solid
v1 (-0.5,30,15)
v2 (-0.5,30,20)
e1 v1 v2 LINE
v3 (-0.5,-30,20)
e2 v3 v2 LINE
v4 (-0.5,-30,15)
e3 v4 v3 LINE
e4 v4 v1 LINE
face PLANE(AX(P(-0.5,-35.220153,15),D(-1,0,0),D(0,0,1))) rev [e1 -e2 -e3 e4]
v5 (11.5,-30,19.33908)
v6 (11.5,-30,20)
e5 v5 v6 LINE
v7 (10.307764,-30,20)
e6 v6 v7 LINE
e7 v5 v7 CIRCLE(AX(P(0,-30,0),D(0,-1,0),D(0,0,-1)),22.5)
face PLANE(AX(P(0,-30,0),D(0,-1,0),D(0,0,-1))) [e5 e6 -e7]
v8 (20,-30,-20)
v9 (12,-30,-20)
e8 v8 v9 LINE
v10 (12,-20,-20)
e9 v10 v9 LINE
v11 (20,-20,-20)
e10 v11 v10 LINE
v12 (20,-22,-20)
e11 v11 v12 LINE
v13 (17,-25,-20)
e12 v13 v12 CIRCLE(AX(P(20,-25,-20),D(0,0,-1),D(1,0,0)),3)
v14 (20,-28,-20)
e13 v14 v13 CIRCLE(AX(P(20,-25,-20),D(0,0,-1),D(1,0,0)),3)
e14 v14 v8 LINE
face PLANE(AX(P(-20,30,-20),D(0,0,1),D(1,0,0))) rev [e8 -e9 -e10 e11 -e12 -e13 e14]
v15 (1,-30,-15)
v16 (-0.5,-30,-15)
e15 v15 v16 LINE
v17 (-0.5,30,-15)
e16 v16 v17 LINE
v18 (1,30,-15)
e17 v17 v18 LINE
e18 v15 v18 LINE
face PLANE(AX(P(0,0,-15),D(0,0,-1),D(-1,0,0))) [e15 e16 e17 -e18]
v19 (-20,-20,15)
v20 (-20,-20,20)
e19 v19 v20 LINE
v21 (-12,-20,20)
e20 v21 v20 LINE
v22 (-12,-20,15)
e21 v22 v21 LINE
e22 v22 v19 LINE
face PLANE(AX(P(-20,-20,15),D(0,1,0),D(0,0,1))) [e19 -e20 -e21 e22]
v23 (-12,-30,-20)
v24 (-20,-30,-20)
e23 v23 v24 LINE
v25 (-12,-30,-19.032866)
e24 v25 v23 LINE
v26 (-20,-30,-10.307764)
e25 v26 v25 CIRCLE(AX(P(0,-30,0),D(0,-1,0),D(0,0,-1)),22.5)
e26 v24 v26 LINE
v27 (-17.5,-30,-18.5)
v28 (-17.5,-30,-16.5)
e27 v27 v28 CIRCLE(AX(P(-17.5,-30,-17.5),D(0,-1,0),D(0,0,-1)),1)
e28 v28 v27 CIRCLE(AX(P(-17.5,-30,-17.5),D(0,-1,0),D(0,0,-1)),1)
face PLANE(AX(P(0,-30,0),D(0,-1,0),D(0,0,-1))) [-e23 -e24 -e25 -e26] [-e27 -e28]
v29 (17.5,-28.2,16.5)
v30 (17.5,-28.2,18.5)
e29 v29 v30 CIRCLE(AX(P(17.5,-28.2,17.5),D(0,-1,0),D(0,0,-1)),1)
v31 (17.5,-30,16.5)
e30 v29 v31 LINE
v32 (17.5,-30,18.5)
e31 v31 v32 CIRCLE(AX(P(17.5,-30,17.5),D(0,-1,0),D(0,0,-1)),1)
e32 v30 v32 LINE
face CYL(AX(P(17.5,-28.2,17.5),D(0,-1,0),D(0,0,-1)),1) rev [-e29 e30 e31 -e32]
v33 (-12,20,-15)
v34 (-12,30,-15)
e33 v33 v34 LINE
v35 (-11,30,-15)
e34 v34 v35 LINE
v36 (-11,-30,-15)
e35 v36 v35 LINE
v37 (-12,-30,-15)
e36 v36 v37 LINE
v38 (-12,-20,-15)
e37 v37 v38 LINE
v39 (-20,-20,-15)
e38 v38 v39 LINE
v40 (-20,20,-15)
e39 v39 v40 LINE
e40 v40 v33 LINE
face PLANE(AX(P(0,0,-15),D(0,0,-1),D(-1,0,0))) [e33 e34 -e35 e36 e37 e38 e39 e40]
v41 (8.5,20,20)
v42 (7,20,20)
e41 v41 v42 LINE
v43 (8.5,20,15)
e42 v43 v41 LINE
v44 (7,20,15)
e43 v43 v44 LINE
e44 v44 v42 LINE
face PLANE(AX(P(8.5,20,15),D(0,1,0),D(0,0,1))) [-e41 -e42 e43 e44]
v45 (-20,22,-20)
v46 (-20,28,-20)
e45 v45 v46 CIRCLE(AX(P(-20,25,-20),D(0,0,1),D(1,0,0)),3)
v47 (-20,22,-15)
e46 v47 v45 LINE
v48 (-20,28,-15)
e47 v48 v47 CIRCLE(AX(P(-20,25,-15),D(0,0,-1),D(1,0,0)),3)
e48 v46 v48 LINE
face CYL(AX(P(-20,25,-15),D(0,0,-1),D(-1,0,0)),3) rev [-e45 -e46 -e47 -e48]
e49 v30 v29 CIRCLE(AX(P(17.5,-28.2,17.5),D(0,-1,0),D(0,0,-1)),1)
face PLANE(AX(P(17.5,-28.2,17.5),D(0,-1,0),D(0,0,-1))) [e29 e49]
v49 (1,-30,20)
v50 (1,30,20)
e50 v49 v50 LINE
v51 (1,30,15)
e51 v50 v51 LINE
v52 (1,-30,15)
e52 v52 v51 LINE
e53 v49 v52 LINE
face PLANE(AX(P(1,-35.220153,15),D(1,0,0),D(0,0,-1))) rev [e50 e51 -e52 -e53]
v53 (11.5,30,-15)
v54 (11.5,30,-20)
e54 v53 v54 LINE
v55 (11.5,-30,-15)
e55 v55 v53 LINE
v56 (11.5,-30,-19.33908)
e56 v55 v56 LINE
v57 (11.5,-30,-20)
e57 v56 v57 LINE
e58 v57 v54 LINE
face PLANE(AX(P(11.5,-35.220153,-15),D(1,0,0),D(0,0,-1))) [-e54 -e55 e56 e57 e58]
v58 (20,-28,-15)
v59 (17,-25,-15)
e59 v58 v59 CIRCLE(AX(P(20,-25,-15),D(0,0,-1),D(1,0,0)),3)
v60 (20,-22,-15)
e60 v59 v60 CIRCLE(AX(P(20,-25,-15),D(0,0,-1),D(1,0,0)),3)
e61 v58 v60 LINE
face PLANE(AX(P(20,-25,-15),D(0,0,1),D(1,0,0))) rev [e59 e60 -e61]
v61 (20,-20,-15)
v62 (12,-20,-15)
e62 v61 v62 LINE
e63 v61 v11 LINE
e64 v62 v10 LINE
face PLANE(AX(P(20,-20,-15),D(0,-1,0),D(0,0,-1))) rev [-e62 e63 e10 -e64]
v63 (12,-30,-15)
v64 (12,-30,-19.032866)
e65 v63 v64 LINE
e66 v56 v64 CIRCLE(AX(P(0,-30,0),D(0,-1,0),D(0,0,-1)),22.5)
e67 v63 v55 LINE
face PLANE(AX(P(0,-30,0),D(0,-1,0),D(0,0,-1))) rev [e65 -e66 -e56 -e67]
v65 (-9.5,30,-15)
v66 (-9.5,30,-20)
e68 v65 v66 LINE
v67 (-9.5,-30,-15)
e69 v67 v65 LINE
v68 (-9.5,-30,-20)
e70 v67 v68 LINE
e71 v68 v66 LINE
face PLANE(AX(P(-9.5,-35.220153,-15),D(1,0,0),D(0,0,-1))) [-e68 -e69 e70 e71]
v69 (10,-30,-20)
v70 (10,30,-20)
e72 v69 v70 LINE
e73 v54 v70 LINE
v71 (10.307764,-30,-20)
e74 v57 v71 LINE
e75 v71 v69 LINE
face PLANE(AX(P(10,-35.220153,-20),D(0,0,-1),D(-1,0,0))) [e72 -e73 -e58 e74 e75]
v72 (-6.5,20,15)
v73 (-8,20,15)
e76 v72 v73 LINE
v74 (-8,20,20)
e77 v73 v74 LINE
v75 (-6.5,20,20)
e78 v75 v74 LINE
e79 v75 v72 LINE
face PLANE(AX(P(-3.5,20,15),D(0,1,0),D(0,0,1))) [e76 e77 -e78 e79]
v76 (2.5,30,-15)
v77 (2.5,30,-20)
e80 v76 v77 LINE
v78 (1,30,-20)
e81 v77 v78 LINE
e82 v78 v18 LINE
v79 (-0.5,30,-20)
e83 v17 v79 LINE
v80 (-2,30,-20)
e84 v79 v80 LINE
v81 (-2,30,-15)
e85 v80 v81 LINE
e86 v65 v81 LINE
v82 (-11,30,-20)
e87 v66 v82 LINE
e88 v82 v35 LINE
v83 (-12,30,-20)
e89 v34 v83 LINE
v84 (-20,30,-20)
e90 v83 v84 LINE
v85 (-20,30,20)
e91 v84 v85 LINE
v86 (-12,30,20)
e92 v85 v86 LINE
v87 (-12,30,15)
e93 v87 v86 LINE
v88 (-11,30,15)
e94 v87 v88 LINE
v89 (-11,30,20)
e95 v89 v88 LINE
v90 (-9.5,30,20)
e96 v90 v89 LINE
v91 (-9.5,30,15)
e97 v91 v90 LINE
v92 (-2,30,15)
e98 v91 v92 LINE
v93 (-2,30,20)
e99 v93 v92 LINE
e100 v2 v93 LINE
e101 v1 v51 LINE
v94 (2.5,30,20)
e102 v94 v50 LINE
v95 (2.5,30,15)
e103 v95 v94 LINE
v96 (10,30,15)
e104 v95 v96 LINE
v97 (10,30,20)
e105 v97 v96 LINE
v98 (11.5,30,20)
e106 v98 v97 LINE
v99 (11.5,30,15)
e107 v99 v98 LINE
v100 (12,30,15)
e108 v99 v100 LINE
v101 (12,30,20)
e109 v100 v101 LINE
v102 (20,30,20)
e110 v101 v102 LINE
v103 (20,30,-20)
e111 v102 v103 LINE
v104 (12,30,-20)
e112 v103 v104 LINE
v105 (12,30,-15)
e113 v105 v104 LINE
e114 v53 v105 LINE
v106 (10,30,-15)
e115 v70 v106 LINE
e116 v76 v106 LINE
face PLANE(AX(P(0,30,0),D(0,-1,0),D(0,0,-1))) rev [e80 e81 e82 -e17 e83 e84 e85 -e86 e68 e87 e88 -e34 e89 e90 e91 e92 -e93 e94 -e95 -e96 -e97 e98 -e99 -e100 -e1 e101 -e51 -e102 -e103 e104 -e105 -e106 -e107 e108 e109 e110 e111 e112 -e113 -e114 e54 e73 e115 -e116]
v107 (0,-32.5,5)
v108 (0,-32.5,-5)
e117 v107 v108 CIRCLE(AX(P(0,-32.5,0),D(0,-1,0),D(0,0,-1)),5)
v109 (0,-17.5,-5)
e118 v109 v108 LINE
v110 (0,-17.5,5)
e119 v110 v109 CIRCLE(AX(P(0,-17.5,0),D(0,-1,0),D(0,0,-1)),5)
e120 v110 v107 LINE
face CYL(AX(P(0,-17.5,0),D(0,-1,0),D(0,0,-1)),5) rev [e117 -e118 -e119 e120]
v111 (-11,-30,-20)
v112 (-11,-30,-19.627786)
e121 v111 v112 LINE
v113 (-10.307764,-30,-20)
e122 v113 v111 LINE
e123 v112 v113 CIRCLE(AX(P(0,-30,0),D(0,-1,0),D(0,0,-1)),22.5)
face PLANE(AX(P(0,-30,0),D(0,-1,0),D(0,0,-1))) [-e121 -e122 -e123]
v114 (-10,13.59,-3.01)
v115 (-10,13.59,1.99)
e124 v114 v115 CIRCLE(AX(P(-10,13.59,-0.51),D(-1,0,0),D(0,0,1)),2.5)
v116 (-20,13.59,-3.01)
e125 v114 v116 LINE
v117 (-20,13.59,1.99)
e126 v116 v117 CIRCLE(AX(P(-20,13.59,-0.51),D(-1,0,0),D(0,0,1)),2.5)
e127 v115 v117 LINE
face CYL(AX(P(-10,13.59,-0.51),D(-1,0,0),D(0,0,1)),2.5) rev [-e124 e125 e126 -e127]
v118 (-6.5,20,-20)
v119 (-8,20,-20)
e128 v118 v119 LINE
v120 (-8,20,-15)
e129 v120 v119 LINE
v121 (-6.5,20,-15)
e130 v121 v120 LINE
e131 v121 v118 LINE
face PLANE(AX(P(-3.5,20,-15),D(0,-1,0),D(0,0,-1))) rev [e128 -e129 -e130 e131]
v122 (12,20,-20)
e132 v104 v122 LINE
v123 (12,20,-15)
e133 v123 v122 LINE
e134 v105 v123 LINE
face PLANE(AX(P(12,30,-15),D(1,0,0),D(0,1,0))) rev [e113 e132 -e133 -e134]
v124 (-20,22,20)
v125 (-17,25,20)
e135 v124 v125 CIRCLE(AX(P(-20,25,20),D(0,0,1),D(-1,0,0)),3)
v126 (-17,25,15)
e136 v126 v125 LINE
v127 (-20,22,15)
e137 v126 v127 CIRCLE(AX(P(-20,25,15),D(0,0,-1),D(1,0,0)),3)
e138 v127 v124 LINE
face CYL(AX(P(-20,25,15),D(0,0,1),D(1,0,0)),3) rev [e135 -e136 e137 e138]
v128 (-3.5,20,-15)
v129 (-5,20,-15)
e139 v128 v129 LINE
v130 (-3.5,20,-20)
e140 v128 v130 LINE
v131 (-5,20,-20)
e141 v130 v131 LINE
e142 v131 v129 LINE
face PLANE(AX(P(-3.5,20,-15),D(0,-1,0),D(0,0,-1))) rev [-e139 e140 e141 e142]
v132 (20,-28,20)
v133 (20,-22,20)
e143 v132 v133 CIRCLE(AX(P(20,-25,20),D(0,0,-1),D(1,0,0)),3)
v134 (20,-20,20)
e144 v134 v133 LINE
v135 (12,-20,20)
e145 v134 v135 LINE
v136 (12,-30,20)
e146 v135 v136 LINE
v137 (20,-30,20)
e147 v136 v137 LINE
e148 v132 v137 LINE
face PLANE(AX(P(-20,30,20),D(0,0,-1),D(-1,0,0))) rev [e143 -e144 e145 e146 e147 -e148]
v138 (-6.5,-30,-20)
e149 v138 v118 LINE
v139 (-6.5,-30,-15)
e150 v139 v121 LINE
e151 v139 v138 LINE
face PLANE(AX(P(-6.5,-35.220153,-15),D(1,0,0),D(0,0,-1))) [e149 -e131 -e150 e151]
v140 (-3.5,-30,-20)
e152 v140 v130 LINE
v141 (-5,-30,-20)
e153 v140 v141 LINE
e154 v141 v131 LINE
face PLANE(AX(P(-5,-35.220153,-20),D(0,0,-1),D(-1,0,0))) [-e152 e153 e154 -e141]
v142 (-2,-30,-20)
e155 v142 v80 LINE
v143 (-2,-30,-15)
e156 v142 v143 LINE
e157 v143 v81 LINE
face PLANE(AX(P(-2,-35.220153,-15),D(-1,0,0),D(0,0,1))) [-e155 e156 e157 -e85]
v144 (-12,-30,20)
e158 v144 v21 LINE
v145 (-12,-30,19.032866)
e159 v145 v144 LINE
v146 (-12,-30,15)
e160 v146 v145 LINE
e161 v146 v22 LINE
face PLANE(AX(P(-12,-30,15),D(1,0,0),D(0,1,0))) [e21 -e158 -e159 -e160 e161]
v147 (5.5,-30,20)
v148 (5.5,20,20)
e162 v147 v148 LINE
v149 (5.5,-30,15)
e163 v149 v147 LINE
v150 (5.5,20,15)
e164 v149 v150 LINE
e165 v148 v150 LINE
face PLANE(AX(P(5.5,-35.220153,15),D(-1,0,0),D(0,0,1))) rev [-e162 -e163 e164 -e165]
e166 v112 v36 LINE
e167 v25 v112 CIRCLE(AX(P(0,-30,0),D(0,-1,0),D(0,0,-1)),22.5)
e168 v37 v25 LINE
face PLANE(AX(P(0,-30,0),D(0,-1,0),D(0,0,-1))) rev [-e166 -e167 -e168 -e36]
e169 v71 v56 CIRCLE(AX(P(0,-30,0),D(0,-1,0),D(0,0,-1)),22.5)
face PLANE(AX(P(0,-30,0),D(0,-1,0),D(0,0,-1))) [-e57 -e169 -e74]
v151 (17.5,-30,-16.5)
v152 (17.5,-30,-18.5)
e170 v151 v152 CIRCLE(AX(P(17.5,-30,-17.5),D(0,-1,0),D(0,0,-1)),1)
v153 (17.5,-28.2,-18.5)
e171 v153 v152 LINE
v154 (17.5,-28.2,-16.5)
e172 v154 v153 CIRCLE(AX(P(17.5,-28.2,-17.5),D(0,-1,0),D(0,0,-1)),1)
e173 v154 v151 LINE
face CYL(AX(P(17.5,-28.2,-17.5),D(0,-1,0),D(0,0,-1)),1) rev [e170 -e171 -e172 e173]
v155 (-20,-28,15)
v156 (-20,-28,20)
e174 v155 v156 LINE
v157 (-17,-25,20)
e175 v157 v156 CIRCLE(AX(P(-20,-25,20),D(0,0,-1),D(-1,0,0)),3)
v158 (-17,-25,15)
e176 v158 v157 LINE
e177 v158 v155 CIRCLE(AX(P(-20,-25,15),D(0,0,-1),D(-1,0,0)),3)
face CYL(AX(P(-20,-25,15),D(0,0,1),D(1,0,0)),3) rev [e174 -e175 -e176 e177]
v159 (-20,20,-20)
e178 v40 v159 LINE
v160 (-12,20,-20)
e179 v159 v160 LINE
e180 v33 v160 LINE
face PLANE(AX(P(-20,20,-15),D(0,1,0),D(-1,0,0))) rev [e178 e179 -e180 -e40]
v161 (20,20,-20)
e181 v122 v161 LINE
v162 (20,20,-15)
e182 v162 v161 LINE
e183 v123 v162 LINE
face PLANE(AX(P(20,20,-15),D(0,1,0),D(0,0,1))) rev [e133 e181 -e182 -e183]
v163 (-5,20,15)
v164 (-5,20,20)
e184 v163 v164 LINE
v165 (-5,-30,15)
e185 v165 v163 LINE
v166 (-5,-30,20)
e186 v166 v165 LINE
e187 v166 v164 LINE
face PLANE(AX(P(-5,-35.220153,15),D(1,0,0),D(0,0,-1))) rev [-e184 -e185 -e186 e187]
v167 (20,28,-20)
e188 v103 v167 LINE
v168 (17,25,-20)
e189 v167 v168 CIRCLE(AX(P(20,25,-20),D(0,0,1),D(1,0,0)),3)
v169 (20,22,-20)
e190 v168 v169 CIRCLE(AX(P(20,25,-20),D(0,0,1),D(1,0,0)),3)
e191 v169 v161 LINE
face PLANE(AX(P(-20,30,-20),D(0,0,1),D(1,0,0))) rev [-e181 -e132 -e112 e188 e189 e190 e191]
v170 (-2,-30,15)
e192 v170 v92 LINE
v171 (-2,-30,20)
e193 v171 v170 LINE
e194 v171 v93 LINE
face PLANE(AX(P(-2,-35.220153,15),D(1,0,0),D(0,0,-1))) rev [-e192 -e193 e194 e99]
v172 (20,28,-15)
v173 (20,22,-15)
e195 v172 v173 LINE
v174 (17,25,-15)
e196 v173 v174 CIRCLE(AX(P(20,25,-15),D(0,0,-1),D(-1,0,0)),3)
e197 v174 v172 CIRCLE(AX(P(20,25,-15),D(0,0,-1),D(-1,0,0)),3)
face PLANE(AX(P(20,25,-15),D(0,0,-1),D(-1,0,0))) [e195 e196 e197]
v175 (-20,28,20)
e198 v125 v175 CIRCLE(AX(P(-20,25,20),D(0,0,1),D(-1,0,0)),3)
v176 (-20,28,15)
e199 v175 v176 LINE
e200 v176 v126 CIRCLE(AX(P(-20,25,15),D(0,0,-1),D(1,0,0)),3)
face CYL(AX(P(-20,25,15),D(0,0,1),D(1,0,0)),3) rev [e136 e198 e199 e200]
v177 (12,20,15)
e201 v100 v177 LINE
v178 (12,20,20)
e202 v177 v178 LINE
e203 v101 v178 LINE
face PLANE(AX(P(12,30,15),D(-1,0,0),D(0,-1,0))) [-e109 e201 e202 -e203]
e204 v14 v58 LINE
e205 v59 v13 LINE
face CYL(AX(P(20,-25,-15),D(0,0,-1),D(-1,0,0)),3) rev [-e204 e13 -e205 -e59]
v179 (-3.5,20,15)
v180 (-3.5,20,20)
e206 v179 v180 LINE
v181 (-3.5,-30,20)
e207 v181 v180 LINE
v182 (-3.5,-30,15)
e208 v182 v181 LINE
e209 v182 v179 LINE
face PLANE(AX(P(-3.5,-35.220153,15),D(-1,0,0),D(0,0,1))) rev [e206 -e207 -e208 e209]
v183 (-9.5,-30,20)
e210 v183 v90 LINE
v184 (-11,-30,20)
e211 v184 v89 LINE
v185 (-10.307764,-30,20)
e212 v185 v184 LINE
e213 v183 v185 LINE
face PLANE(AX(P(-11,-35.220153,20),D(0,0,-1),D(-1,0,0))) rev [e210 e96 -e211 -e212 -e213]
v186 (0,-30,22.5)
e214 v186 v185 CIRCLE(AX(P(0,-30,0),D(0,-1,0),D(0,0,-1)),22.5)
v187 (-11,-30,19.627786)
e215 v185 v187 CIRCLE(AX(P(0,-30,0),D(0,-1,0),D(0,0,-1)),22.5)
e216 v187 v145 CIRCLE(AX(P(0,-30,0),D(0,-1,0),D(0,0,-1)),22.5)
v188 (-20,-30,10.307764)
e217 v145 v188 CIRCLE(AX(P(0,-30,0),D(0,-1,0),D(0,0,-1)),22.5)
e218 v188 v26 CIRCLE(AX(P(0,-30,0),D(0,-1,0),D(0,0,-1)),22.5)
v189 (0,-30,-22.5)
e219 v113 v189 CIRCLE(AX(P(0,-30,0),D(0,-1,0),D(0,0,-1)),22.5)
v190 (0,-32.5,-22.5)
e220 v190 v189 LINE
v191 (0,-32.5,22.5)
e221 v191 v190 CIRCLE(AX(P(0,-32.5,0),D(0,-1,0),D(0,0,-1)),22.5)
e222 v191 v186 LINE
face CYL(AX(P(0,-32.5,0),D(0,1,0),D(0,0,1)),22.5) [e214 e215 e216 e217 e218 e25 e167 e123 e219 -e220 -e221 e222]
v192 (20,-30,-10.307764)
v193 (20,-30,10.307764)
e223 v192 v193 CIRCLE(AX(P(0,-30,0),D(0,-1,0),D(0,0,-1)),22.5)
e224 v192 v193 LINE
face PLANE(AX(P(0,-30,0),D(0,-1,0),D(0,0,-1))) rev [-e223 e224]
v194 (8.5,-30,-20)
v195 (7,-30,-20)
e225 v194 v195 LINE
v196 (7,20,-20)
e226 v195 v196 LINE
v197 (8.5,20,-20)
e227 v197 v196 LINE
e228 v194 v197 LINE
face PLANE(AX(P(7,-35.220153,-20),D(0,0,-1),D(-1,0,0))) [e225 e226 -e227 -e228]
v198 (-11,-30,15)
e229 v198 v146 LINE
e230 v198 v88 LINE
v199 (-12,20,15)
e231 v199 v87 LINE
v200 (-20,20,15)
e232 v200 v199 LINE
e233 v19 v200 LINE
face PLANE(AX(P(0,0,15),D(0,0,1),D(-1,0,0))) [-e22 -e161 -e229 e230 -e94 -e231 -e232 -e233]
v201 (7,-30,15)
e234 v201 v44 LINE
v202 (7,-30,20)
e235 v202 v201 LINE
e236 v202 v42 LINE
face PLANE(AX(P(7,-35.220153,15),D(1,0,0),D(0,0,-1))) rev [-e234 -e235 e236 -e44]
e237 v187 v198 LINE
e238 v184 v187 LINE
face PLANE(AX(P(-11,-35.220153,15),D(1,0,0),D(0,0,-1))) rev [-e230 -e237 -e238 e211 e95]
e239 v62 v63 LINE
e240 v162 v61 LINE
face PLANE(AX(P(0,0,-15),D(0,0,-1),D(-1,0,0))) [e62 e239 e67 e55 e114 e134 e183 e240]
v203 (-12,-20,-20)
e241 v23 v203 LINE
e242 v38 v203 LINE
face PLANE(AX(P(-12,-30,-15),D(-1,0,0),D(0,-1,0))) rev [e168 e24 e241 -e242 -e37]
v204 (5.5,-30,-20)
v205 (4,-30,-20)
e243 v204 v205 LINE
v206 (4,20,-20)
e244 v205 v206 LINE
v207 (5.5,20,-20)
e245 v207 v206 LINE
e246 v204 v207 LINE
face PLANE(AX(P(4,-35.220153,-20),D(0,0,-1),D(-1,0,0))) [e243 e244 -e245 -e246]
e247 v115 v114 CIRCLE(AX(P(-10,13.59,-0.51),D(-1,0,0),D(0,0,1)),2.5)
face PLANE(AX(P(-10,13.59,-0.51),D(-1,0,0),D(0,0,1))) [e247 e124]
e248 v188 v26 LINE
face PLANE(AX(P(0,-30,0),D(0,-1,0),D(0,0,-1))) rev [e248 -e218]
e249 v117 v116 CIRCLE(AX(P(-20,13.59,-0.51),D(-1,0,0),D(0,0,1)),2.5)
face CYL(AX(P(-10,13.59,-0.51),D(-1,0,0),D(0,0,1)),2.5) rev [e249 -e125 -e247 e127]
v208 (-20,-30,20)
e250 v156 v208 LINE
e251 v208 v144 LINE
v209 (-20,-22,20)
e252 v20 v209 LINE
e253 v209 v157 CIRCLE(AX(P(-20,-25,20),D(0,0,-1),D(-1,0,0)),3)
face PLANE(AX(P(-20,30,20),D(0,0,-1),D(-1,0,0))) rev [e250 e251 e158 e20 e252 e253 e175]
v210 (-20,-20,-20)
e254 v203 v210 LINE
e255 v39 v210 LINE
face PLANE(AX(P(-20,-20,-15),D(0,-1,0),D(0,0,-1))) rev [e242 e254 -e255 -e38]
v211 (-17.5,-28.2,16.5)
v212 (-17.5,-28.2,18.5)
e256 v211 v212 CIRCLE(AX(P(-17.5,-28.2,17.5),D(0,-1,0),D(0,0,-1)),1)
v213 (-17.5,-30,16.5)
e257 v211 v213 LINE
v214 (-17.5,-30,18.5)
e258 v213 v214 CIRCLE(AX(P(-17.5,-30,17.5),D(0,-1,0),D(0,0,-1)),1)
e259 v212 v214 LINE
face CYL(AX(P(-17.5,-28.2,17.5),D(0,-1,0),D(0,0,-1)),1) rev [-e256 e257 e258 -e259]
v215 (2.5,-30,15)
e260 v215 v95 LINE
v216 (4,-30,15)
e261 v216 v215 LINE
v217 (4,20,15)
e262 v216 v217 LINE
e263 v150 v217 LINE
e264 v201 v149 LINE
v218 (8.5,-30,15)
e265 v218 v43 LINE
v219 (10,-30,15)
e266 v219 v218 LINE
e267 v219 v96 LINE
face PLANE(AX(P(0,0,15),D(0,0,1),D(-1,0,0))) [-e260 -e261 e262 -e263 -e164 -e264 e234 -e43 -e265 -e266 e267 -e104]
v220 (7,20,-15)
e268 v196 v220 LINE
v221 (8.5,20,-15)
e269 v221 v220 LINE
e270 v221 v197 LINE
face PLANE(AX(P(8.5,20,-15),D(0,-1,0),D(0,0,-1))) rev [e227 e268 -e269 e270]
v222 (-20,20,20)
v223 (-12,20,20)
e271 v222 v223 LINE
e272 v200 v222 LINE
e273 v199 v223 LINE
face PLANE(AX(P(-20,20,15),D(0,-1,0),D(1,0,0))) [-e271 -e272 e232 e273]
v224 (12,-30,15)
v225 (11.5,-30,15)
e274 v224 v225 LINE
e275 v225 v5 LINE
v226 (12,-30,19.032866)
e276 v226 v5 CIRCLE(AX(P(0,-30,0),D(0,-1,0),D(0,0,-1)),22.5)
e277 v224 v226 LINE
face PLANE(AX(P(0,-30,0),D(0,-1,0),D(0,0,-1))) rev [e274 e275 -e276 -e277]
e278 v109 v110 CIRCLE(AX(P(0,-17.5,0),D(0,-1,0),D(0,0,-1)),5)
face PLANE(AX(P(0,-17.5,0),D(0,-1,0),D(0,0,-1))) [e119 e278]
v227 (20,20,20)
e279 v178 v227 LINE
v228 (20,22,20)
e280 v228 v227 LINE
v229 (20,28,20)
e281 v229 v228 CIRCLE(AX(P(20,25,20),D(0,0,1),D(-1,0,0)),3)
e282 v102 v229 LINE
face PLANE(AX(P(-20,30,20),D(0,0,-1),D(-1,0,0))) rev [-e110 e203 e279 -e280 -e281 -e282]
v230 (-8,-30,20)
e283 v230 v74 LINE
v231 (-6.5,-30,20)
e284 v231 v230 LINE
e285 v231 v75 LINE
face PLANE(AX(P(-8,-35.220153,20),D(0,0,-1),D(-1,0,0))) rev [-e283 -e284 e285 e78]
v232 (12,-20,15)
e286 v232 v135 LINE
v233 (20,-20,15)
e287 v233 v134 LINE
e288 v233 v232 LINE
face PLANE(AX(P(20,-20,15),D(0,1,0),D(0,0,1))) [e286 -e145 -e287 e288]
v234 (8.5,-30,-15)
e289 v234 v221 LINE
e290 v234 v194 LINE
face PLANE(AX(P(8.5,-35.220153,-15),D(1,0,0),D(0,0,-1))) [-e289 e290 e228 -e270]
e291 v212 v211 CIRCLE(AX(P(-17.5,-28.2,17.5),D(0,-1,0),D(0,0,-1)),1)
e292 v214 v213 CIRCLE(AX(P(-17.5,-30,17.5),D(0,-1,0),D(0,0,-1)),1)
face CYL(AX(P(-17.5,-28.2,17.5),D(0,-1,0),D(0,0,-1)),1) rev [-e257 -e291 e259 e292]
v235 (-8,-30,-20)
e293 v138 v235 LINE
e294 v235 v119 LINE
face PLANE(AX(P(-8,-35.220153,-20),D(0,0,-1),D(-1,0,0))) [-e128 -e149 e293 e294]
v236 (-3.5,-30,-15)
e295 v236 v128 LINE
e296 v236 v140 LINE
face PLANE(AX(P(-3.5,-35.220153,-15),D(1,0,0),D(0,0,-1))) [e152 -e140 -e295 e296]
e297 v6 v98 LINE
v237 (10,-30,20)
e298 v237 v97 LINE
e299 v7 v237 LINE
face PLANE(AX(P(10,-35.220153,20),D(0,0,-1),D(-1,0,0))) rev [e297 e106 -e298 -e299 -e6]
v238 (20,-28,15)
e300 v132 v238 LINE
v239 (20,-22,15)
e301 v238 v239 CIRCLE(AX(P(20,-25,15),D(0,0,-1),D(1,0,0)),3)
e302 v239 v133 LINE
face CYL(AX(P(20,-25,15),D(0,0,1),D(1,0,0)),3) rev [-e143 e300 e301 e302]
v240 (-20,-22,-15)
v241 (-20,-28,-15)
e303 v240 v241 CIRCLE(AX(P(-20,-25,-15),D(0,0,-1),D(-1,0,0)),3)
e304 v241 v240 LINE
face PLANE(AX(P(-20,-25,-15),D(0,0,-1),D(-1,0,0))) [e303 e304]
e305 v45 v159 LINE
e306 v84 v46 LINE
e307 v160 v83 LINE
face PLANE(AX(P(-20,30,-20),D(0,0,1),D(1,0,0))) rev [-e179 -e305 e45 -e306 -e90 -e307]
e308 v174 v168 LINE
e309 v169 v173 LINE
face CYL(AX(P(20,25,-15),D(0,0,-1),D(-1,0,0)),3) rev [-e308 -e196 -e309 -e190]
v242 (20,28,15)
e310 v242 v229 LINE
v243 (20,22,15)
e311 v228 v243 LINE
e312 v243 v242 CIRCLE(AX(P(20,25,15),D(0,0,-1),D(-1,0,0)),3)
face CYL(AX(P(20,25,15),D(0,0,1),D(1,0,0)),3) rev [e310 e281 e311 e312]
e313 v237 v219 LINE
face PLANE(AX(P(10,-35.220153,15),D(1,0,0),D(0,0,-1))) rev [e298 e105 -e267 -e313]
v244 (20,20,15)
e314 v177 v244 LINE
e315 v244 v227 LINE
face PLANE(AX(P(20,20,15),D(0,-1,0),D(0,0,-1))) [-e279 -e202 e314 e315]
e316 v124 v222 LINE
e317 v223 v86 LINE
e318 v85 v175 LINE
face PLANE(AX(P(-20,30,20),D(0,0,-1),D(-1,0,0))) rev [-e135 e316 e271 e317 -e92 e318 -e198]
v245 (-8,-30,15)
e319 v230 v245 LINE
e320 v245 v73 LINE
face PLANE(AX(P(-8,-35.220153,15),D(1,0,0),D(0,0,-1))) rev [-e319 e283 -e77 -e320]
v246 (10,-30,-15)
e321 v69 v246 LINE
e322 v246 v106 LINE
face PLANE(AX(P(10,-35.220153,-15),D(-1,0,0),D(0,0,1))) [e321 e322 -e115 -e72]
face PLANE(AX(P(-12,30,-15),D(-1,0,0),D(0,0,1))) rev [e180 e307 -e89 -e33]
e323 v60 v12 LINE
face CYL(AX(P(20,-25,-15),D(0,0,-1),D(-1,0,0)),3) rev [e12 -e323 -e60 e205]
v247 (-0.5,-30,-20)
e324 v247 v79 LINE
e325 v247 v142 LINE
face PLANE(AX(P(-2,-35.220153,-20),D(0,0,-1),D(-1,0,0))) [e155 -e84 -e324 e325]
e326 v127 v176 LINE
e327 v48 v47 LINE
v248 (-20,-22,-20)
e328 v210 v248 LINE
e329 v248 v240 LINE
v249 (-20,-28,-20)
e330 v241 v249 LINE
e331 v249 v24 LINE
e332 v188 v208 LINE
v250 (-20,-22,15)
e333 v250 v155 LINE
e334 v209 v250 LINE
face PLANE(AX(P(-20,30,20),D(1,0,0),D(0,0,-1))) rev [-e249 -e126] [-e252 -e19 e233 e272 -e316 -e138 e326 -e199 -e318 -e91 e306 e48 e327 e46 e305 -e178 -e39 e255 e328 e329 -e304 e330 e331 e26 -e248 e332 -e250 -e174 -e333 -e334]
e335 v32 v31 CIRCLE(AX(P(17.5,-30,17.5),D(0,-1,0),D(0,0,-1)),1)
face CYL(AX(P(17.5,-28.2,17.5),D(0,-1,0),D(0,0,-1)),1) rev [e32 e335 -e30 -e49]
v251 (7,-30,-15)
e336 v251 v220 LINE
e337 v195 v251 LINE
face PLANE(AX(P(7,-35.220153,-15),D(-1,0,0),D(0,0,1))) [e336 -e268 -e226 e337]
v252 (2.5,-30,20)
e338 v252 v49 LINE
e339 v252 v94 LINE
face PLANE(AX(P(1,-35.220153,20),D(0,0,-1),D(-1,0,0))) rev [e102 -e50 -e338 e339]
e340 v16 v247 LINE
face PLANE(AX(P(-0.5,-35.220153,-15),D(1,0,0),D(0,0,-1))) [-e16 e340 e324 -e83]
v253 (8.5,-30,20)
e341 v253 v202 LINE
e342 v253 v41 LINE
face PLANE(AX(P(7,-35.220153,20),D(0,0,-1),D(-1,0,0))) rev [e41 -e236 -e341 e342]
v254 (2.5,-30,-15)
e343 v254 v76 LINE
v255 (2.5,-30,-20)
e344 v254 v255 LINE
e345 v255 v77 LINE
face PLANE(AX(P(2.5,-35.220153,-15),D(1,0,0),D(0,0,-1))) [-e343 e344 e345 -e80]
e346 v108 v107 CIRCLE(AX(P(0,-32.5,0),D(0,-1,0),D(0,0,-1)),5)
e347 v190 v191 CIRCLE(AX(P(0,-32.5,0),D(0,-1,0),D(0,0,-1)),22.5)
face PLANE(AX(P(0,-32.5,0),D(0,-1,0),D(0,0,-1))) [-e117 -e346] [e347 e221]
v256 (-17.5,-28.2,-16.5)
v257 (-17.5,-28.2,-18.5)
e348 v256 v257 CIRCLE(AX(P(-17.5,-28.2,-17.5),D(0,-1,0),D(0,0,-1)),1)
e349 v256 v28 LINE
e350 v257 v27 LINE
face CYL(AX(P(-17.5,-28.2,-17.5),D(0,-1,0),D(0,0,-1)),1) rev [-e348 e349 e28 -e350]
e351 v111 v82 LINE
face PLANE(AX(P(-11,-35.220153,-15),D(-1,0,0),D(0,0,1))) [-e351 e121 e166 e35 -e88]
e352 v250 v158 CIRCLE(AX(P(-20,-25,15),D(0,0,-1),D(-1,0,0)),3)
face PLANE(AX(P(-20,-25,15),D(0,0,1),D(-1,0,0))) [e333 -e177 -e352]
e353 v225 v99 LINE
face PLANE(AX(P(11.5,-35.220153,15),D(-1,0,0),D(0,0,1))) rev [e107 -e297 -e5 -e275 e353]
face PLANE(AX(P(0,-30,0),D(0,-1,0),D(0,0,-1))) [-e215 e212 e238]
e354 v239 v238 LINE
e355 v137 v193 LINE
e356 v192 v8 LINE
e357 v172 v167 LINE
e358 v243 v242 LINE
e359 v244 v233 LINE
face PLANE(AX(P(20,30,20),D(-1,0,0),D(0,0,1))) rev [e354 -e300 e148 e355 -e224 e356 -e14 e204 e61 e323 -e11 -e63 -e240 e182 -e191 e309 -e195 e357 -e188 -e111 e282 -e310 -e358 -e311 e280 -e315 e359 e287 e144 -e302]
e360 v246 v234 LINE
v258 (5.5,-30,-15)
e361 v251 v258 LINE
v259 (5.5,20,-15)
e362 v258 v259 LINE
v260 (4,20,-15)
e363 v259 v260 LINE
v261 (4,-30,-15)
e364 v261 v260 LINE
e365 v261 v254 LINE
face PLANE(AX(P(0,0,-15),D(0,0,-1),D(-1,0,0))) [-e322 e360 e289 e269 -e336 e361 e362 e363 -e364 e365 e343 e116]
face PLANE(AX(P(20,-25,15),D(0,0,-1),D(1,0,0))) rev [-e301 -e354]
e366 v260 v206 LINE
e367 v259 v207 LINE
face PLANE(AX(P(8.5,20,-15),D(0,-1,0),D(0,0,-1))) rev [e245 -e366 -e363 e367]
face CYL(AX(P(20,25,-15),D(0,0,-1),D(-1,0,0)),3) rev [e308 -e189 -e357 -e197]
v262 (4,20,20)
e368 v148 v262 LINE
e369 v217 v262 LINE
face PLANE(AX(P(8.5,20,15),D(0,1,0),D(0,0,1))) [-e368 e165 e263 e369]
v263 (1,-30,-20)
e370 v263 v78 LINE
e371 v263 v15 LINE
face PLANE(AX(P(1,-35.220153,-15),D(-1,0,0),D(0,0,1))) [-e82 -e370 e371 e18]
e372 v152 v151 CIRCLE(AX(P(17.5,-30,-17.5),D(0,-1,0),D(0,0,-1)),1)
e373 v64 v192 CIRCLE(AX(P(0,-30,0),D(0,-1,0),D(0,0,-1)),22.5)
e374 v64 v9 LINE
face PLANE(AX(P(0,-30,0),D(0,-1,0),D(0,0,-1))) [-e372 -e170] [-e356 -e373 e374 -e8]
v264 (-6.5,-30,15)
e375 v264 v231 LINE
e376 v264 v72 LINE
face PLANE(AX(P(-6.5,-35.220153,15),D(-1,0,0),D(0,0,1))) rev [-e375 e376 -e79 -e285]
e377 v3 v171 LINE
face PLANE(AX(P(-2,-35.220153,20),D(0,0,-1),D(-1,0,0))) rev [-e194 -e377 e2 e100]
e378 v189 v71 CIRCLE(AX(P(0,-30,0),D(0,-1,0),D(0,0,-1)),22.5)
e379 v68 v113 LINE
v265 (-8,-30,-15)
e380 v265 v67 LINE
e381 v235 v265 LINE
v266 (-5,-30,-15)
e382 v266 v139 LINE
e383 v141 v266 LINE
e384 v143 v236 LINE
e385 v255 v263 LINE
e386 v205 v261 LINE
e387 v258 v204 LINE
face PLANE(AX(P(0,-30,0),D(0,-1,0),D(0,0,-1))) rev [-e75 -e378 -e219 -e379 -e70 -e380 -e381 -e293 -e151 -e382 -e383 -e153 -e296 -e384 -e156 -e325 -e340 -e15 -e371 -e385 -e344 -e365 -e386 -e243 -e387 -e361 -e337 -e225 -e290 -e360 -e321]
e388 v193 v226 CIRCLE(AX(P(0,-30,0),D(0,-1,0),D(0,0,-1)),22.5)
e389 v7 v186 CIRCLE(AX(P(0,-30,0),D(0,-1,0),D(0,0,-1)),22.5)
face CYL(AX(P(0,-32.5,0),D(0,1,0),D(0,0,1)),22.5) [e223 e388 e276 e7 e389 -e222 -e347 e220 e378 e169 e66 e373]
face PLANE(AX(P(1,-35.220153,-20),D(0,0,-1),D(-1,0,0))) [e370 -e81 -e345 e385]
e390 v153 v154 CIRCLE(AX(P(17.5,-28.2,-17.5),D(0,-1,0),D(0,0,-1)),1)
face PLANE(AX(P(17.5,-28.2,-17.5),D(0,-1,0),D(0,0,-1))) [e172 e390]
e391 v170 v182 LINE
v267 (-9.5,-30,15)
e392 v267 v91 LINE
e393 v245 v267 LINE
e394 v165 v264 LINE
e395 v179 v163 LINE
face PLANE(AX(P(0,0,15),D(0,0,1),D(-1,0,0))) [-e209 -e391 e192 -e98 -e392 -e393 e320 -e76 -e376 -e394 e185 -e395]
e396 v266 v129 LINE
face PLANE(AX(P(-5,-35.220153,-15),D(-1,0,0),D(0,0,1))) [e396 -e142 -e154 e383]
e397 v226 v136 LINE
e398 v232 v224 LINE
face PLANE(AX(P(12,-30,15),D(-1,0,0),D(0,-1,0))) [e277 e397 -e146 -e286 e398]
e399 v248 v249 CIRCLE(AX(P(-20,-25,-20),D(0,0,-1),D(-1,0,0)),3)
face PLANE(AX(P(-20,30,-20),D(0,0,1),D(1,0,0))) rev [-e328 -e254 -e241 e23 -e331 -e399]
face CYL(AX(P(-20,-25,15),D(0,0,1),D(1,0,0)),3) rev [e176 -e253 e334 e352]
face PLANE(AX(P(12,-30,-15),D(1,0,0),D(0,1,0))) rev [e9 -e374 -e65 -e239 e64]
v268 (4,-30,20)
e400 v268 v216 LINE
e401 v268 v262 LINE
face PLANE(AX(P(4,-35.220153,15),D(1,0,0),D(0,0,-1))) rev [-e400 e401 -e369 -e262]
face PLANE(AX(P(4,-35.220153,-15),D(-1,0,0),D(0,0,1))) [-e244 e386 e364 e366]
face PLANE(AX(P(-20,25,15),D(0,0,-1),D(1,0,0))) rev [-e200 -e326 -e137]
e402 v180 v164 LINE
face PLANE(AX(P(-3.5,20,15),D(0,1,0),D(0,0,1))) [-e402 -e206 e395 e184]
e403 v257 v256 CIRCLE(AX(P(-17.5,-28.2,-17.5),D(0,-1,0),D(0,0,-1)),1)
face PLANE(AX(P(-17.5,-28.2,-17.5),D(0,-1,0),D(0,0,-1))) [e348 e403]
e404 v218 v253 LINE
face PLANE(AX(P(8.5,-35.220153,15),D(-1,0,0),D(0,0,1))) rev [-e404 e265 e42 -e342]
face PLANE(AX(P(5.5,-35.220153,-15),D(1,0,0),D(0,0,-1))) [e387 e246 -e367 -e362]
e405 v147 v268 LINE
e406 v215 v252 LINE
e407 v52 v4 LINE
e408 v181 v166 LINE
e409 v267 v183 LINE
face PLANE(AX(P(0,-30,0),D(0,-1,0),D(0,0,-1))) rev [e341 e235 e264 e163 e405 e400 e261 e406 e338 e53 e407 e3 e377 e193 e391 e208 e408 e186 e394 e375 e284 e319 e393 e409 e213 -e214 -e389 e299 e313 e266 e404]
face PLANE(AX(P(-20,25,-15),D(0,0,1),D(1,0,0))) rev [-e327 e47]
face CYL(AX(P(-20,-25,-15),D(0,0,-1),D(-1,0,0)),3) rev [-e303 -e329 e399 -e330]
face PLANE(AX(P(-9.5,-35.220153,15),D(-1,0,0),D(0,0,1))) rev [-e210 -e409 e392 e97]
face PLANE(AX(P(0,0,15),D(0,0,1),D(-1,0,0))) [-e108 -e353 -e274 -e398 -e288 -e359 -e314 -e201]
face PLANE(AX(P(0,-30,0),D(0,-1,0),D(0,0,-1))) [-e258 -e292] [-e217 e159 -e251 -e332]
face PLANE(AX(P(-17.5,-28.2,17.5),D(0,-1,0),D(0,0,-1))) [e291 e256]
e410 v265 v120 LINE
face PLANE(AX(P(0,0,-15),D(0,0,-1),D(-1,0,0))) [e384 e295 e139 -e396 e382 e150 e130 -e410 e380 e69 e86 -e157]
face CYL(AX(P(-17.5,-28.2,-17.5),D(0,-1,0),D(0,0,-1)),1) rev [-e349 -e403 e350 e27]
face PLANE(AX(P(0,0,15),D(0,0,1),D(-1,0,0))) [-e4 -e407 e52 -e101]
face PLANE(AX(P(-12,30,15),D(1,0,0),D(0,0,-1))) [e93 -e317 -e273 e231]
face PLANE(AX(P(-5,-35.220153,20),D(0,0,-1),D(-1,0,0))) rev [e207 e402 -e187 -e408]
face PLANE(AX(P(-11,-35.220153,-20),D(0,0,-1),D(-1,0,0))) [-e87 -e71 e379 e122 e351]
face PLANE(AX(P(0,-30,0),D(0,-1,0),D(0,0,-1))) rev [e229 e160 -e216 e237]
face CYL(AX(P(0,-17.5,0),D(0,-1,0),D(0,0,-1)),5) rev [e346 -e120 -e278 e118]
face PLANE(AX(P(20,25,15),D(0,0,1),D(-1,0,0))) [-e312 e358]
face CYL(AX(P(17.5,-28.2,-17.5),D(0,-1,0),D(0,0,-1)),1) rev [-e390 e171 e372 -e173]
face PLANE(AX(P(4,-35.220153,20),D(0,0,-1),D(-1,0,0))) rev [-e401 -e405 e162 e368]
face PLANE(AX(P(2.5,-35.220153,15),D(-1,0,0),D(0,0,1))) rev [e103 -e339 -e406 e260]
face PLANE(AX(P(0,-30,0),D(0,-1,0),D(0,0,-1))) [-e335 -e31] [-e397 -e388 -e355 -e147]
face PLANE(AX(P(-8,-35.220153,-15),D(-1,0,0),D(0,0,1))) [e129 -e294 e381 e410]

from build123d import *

# Parameters (mm, degrees)
SKETCH1_W           = 40
SKETCH1_H           = 40
BOSS_EXTRUDE1_DEPTH = 30
CUT_EXTRUDE1_DEPTH  = 5
SKETCH3_W           = 1.5
SKETCH3_H           = 5
BOSS_EXTRUDE2_DEPTH = 60
SKETCH4_W           = 4.5
SKETCH4_H           = 10
CUT_EXTRUDE2_DEPTH  = 5
SKETCH5_R           = 3
CUT_EXTRUDE3_DEPTH  = 5
SKETCH6_R           = 22.5
BOSS_EXTRUDE3_DEPTH = 2.5
SKETCH7_R           = 5
CUT_EXTRUDE4_DEPTH  = 15
SKETCH8_R           = 2.5
CUT_EXTRUDE5_DEPTH  = 10
SKETCH9_R           = 1
CUT_EXTRUDE6_DEPTH  = 1.8


with BuildPart() as part:
    # Sketch1 → Boss-Extrude1 (new, symmetric)
    with BuildSketch(Plane(origin=(0, 0, 0), x_dir=(1, 0, 0), z_dir=(0, 1, 0))):
        Rectangle(SKETCH1_W, SKETCH1_H)
    extrude(amount=BOSS_EXTRUDE1_DEPTH, both=True)

    # Sketch2 → Cut-Extrude1 (cut)
    with BuildSketch(Plane(origin=(0, 0, -20), x_dir=(-1, 0, 0), z_dir=(0, 0, -1))):
        Polygon((-12, 30), (12, 30), (12, 20), (20, 20), (20, -20), (12, -20), (12, -30), (-12, -30), (-12, -20), (-20, -20), (-20, 20), (-12, 20), align=None)
    cut_extrude1 = extrude(amount=-CUT_EXTRUDE1_DEPTH, mode=Mode.SUBTRACT)

    # Mirror1: Cut-Extrude1 across plane
    add(cut_extrude1.mirror(Plane.XY), mode=Mode.SUBTRACT)

    # Sketch3 → Boss-Extrude2 (add)
    with BuildSketch(Plane(origin=(0, 30, 0), x_dir=(1, 0, 0), z_dir=(0, 1, 0))):
        with Locations((-10.25, 17.5)):
            Rectangle(SKETCH3_W, SKETCH3_H)
        with Locations((-7.25, 17.5)):
            Rectangle(SKETCH3_W, SKETCH3_H)
        with Locations((-4.25, 17.5)):
            Rectangle(SKETCH3_W, SKETCH3_H)
        with Locations((-1.25, 17.5)):
            Rectangle(SKETCH3_W, SKETCH3_H)
        with Locations((1.75, 17.5)):
            Rectangle(SKETCH3_W, SKETCH3_H)
        with Locations((4.75, 17.5)):
            Rectangle(SKETCH3_W, SKETCH3_H)
        with Locations((7.75, 17.5)):
            Rectangle(SKETCH3_W, SKETCH3_H)
        with Locations((10.75, 17.5)):
            Rectangle(SKETCH3_W, SKETCH3_H)
    boss_extrude2 = extrude(amount=-BOSS_EXTRUDE2_DEPTH)

    # Sketch4 → Cut-Extrude2 (cut)
    with BuildSketch(Plane(origin=(0, 0, -20), x_dir=(-1, 0, 0), z_dir=(0, 0, -1))):
        with Locations((-6.25, 25)):
            Rectangle(SKETCH4_W, SKETCH4_H)
        with Locations((5.75, 25)):
            Rectangle(SKETCH4_W, SKETCH4_H)
    cut_extrude2 = extrude(amount=-CUT_EXTRUDE2_DEPTH, mode=Mode.SUBTRACT)

    # Mirror2: Boss-Extrude2, Cut-Extrude2 across plane
    add(boss_extrude2.mirror(Plane.XY))
    add(cut_extrude2.mirror(Plane.XY), mode=Mode.SUBTRACT)

    # Sketch5 → Cut-Extrude3 (cut)
    with BuildSketch(Plane(origin=(0, 0, -20), x_dir=(-1, 0, 0), z_dir=(0, 0, -1))):
        with Locations((-20, 25)):
            Circle(SKETCH5_R)
        with Locations((20, 25)):
            Circle(SKETCH5_R)
        with Locations((-20, -25)):
            Circle(SKETCH5_R)
        with Locations((20, -25)):
            Circle(SKETCH5_R)
    cut_extrude3 = extrude(amount=-CUT_EXTRUDE3_DEPTH, mode=Mode.SUBTRACT)

    # Mirror3: Cut-Extrude3 across plane
    add(cut_extrude3.mirror(Plane.XY), mode=Mode.SUBTRACT)

    # Sketch6 → Boss-Extrude3 (add)
    with BuildSketch(Plane.XZ.offset(30)):
        with Locations(Location((0, 0, 0), (0, 0, 62.733955549))):
            Circle(SKETCH6_R)
    extrude(amount=BOSS_EXTRUDE3_DEPTH)

    # Sketch7 → Cut-Extrude4 (cut)
    with BuildSketch(Plane.XZ.offset(32.5)):
        with Locations(Location((0, 0, 0), (0, 0, 270))):
            Circle(SKETCH7_R)
    extrude(amount=-CUT_EXTRUDE4_DEPTH, mode=Mode.SUBTRACT)

    # Sketch8 → Cut-Extrude5 (cut)
    with BuildSketch(Plane.ZY.offset(20)):
        with Locations((-0.51, 13.59)):
            Circle(SKETCH8_R)
    extrude(amount=-CUT_EXTRUDE5_DEPTH, mode=Mode.SUBTRACT)

    # Sketch9 → Cut-Extrude6 (cut)
    with BuildSketch(Plane.XZ.offset(30)):
        with Locations(Location((-17.5, 17.5, 0), (0, 0, 270))):
            Circle(SKETCH9_R)
        with Locations(Location((17.5, 17.5, 0), (0, 0, 270))):
            Circle(SKETCH9_R)
        with Locations(Location((17.5, -17.5, 0), (0, 0, 270))):
            Circle(SKETCH9_R)
        with Locations(Location((-17.5, -17.5, 0), (0, 0, 270))):
            Circle(SKETCH9_R)
    extrude(amount=-CUT_EXTRUDE6_DEPTH, mode=Mode.SUBTRACT)


solid = part.part
